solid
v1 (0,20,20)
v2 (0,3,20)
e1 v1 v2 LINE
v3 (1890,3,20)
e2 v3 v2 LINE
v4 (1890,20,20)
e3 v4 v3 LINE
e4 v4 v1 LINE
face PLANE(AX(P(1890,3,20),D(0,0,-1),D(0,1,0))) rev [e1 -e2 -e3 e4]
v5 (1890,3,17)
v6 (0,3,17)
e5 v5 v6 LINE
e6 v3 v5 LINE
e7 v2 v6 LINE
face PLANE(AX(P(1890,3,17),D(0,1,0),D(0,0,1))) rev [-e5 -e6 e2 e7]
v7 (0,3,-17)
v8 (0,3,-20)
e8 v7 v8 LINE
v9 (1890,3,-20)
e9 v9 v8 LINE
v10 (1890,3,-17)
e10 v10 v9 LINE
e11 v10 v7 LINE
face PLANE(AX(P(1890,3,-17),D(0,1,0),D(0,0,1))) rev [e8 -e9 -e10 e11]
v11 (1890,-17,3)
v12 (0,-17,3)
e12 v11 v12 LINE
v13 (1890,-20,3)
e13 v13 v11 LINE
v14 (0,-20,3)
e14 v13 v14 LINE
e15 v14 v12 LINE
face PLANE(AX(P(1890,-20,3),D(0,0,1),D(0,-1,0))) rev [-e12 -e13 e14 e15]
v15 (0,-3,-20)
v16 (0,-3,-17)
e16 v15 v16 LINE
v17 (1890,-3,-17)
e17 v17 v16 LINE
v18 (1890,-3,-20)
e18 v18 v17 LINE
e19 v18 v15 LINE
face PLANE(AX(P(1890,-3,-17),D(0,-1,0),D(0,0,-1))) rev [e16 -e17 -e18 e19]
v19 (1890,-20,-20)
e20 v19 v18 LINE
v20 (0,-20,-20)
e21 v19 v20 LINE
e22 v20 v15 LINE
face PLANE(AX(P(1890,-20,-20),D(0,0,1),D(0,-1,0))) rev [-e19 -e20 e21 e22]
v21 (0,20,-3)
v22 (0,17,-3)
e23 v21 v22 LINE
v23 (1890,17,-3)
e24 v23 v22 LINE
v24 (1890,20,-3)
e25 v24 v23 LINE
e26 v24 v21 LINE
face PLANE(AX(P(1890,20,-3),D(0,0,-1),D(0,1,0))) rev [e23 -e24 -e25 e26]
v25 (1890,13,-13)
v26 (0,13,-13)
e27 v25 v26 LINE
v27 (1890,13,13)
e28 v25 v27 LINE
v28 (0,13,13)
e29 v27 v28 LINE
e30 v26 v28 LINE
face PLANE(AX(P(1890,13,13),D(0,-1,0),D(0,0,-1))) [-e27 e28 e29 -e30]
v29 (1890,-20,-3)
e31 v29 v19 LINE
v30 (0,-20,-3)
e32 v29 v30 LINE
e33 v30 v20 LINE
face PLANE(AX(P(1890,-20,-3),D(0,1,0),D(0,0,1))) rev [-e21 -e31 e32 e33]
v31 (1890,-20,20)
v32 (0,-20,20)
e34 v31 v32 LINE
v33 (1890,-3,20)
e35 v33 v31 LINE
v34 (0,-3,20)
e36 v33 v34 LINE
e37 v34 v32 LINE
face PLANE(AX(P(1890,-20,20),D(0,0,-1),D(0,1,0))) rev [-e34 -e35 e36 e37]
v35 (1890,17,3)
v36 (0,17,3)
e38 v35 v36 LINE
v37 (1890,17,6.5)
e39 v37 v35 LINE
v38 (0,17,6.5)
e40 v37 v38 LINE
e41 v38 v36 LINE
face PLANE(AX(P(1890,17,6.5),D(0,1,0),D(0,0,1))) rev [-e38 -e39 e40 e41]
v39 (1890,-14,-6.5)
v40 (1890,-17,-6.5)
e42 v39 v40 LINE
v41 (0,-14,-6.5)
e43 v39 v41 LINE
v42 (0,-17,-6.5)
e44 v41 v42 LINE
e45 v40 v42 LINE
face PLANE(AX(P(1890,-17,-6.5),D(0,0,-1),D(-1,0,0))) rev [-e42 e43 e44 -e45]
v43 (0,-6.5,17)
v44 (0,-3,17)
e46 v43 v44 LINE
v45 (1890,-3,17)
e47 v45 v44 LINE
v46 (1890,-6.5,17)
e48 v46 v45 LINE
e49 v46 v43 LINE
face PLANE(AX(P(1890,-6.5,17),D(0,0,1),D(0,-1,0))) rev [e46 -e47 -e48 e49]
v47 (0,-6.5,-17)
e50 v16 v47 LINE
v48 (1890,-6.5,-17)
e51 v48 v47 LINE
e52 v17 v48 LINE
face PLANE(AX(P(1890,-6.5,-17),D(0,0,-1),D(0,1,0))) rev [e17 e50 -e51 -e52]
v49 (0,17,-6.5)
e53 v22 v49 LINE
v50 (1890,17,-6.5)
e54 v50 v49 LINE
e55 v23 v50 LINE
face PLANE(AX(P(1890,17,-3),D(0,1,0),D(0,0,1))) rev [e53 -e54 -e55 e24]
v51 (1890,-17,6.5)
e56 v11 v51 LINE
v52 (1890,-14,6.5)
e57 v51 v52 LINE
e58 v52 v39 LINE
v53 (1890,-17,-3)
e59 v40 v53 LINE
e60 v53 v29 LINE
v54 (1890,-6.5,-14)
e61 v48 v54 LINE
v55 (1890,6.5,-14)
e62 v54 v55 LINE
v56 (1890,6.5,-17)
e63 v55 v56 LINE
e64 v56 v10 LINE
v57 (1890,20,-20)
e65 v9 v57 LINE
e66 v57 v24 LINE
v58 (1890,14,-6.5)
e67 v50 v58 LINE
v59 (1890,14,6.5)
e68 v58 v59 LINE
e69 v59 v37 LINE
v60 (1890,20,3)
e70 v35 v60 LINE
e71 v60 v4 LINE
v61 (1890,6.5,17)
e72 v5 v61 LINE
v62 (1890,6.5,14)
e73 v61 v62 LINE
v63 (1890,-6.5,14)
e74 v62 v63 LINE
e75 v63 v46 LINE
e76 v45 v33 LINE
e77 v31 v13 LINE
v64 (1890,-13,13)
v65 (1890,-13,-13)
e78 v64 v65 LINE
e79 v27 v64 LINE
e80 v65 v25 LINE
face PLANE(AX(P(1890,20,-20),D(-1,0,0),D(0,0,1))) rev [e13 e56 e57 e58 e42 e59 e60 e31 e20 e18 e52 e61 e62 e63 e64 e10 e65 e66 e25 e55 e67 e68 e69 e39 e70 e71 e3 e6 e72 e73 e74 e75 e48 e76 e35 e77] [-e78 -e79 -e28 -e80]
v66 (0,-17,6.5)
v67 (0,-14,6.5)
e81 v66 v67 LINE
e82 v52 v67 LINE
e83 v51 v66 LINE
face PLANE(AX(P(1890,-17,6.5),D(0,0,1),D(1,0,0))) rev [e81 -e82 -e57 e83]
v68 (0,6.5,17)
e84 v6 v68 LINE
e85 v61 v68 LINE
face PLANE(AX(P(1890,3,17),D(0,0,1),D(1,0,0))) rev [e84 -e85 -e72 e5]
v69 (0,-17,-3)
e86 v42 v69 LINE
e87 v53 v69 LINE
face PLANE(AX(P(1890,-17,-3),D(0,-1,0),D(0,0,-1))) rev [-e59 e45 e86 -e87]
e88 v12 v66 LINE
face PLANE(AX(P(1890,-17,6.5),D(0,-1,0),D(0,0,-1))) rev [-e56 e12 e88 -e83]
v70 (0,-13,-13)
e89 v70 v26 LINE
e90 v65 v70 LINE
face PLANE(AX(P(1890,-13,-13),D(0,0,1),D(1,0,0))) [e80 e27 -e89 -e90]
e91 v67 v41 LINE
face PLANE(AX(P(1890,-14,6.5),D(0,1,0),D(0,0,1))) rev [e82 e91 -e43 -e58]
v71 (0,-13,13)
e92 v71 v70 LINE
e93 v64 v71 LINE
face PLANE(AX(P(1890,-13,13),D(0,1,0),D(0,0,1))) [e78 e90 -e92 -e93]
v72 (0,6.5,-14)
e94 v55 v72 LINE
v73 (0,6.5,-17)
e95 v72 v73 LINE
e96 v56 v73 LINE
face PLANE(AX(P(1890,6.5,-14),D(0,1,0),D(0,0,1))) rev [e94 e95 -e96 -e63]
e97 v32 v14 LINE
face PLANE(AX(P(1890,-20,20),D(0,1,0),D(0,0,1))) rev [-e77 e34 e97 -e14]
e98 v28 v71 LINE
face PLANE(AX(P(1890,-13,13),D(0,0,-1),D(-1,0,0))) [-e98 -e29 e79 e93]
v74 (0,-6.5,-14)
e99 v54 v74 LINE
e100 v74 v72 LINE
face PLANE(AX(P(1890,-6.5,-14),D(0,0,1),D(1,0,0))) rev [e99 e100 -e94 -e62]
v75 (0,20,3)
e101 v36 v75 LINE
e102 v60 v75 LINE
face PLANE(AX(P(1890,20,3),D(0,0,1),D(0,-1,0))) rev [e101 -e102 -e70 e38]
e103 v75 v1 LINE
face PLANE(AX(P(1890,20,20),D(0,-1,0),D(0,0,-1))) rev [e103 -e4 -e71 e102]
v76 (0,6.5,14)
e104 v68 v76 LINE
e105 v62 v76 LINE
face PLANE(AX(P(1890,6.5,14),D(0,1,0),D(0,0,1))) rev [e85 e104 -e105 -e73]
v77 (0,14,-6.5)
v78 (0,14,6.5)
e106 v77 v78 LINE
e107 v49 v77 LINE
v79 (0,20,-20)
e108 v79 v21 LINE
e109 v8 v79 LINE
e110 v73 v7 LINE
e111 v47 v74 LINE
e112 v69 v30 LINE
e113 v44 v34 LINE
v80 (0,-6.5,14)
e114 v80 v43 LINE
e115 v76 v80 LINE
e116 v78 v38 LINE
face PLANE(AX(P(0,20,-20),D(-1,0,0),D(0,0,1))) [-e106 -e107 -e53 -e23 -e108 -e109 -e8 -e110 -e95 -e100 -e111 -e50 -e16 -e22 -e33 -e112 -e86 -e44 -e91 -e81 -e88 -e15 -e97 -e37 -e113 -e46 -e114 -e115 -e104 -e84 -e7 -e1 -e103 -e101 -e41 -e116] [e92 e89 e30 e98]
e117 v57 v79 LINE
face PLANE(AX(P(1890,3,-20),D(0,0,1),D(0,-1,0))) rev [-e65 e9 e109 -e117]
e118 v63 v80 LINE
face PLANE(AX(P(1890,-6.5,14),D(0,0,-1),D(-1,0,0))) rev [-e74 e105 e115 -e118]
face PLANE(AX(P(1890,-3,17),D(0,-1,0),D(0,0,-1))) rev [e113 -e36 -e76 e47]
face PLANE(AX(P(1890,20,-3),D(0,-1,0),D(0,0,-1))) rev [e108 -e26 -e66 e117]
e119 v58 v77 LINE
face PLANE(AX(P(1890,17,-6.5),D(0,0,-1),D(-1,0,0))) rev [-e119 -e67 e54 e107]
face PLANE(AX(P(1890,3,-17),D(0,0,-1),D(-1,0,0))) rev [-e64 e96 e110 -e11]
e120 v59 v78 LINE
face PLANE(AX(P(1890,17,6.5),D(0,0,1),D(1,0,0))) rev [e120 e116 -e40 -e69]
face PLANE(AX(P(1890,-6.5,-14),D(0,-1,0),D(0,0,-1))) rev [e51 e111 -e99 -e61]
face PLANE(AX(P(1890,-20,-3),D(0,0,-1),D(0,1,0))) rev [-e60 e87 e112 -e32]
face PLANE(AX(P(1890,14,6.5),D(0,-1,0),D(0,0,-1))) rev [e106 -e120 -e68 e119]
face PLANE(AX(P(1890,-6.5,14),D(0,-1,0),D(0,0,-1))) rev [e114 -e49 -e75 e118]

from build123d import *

# Parameters (mm, degrees)
SKETCH1_W           = 26
SKETCH1_H           = 26
BOSS_EXTRUDE1_DEPTH = 1890


with BuildPart() as part:
    # Sketch1 → Boss-Extrude1 (new body)
    with BuildSketch(Plane(origin=(0, 0, 0), x_dir=(0, 0, -1), z_dir=(1, 0, 0))):
        Polygon((-20, -20), (-3, -20), (-3, -17), (-6.5, -17), (-6.5, -14), (6.5, -14), (6.5, -17), (3, -17), (3, -20), (20, -20), (20, -3), (17, -3), (17, -6.5), (14, -6.5), (14, 6.5), (17, 6.5), (17, 3), (20, 3), (20, 20), (3, 20), (3, 17), (6.5, 17), (6.5, 14), (-6.5, 14), (-6.5, 17), (-3, 17), (-3, 20), (-20, 20), (-20, 3), (-17, 3), (-17, 6.5), (-14, 6.5), (-14, -6.5), (-17, -6.5), (-17, -3), (-20, -3), align=None)
        Rectangle(SKETCH1_W, SKETCH1_H, mode=Mode.SUBTRACT)
    extrude(amount=BOSS_EXTRUDE1_DEPTH)


solid = part.part
